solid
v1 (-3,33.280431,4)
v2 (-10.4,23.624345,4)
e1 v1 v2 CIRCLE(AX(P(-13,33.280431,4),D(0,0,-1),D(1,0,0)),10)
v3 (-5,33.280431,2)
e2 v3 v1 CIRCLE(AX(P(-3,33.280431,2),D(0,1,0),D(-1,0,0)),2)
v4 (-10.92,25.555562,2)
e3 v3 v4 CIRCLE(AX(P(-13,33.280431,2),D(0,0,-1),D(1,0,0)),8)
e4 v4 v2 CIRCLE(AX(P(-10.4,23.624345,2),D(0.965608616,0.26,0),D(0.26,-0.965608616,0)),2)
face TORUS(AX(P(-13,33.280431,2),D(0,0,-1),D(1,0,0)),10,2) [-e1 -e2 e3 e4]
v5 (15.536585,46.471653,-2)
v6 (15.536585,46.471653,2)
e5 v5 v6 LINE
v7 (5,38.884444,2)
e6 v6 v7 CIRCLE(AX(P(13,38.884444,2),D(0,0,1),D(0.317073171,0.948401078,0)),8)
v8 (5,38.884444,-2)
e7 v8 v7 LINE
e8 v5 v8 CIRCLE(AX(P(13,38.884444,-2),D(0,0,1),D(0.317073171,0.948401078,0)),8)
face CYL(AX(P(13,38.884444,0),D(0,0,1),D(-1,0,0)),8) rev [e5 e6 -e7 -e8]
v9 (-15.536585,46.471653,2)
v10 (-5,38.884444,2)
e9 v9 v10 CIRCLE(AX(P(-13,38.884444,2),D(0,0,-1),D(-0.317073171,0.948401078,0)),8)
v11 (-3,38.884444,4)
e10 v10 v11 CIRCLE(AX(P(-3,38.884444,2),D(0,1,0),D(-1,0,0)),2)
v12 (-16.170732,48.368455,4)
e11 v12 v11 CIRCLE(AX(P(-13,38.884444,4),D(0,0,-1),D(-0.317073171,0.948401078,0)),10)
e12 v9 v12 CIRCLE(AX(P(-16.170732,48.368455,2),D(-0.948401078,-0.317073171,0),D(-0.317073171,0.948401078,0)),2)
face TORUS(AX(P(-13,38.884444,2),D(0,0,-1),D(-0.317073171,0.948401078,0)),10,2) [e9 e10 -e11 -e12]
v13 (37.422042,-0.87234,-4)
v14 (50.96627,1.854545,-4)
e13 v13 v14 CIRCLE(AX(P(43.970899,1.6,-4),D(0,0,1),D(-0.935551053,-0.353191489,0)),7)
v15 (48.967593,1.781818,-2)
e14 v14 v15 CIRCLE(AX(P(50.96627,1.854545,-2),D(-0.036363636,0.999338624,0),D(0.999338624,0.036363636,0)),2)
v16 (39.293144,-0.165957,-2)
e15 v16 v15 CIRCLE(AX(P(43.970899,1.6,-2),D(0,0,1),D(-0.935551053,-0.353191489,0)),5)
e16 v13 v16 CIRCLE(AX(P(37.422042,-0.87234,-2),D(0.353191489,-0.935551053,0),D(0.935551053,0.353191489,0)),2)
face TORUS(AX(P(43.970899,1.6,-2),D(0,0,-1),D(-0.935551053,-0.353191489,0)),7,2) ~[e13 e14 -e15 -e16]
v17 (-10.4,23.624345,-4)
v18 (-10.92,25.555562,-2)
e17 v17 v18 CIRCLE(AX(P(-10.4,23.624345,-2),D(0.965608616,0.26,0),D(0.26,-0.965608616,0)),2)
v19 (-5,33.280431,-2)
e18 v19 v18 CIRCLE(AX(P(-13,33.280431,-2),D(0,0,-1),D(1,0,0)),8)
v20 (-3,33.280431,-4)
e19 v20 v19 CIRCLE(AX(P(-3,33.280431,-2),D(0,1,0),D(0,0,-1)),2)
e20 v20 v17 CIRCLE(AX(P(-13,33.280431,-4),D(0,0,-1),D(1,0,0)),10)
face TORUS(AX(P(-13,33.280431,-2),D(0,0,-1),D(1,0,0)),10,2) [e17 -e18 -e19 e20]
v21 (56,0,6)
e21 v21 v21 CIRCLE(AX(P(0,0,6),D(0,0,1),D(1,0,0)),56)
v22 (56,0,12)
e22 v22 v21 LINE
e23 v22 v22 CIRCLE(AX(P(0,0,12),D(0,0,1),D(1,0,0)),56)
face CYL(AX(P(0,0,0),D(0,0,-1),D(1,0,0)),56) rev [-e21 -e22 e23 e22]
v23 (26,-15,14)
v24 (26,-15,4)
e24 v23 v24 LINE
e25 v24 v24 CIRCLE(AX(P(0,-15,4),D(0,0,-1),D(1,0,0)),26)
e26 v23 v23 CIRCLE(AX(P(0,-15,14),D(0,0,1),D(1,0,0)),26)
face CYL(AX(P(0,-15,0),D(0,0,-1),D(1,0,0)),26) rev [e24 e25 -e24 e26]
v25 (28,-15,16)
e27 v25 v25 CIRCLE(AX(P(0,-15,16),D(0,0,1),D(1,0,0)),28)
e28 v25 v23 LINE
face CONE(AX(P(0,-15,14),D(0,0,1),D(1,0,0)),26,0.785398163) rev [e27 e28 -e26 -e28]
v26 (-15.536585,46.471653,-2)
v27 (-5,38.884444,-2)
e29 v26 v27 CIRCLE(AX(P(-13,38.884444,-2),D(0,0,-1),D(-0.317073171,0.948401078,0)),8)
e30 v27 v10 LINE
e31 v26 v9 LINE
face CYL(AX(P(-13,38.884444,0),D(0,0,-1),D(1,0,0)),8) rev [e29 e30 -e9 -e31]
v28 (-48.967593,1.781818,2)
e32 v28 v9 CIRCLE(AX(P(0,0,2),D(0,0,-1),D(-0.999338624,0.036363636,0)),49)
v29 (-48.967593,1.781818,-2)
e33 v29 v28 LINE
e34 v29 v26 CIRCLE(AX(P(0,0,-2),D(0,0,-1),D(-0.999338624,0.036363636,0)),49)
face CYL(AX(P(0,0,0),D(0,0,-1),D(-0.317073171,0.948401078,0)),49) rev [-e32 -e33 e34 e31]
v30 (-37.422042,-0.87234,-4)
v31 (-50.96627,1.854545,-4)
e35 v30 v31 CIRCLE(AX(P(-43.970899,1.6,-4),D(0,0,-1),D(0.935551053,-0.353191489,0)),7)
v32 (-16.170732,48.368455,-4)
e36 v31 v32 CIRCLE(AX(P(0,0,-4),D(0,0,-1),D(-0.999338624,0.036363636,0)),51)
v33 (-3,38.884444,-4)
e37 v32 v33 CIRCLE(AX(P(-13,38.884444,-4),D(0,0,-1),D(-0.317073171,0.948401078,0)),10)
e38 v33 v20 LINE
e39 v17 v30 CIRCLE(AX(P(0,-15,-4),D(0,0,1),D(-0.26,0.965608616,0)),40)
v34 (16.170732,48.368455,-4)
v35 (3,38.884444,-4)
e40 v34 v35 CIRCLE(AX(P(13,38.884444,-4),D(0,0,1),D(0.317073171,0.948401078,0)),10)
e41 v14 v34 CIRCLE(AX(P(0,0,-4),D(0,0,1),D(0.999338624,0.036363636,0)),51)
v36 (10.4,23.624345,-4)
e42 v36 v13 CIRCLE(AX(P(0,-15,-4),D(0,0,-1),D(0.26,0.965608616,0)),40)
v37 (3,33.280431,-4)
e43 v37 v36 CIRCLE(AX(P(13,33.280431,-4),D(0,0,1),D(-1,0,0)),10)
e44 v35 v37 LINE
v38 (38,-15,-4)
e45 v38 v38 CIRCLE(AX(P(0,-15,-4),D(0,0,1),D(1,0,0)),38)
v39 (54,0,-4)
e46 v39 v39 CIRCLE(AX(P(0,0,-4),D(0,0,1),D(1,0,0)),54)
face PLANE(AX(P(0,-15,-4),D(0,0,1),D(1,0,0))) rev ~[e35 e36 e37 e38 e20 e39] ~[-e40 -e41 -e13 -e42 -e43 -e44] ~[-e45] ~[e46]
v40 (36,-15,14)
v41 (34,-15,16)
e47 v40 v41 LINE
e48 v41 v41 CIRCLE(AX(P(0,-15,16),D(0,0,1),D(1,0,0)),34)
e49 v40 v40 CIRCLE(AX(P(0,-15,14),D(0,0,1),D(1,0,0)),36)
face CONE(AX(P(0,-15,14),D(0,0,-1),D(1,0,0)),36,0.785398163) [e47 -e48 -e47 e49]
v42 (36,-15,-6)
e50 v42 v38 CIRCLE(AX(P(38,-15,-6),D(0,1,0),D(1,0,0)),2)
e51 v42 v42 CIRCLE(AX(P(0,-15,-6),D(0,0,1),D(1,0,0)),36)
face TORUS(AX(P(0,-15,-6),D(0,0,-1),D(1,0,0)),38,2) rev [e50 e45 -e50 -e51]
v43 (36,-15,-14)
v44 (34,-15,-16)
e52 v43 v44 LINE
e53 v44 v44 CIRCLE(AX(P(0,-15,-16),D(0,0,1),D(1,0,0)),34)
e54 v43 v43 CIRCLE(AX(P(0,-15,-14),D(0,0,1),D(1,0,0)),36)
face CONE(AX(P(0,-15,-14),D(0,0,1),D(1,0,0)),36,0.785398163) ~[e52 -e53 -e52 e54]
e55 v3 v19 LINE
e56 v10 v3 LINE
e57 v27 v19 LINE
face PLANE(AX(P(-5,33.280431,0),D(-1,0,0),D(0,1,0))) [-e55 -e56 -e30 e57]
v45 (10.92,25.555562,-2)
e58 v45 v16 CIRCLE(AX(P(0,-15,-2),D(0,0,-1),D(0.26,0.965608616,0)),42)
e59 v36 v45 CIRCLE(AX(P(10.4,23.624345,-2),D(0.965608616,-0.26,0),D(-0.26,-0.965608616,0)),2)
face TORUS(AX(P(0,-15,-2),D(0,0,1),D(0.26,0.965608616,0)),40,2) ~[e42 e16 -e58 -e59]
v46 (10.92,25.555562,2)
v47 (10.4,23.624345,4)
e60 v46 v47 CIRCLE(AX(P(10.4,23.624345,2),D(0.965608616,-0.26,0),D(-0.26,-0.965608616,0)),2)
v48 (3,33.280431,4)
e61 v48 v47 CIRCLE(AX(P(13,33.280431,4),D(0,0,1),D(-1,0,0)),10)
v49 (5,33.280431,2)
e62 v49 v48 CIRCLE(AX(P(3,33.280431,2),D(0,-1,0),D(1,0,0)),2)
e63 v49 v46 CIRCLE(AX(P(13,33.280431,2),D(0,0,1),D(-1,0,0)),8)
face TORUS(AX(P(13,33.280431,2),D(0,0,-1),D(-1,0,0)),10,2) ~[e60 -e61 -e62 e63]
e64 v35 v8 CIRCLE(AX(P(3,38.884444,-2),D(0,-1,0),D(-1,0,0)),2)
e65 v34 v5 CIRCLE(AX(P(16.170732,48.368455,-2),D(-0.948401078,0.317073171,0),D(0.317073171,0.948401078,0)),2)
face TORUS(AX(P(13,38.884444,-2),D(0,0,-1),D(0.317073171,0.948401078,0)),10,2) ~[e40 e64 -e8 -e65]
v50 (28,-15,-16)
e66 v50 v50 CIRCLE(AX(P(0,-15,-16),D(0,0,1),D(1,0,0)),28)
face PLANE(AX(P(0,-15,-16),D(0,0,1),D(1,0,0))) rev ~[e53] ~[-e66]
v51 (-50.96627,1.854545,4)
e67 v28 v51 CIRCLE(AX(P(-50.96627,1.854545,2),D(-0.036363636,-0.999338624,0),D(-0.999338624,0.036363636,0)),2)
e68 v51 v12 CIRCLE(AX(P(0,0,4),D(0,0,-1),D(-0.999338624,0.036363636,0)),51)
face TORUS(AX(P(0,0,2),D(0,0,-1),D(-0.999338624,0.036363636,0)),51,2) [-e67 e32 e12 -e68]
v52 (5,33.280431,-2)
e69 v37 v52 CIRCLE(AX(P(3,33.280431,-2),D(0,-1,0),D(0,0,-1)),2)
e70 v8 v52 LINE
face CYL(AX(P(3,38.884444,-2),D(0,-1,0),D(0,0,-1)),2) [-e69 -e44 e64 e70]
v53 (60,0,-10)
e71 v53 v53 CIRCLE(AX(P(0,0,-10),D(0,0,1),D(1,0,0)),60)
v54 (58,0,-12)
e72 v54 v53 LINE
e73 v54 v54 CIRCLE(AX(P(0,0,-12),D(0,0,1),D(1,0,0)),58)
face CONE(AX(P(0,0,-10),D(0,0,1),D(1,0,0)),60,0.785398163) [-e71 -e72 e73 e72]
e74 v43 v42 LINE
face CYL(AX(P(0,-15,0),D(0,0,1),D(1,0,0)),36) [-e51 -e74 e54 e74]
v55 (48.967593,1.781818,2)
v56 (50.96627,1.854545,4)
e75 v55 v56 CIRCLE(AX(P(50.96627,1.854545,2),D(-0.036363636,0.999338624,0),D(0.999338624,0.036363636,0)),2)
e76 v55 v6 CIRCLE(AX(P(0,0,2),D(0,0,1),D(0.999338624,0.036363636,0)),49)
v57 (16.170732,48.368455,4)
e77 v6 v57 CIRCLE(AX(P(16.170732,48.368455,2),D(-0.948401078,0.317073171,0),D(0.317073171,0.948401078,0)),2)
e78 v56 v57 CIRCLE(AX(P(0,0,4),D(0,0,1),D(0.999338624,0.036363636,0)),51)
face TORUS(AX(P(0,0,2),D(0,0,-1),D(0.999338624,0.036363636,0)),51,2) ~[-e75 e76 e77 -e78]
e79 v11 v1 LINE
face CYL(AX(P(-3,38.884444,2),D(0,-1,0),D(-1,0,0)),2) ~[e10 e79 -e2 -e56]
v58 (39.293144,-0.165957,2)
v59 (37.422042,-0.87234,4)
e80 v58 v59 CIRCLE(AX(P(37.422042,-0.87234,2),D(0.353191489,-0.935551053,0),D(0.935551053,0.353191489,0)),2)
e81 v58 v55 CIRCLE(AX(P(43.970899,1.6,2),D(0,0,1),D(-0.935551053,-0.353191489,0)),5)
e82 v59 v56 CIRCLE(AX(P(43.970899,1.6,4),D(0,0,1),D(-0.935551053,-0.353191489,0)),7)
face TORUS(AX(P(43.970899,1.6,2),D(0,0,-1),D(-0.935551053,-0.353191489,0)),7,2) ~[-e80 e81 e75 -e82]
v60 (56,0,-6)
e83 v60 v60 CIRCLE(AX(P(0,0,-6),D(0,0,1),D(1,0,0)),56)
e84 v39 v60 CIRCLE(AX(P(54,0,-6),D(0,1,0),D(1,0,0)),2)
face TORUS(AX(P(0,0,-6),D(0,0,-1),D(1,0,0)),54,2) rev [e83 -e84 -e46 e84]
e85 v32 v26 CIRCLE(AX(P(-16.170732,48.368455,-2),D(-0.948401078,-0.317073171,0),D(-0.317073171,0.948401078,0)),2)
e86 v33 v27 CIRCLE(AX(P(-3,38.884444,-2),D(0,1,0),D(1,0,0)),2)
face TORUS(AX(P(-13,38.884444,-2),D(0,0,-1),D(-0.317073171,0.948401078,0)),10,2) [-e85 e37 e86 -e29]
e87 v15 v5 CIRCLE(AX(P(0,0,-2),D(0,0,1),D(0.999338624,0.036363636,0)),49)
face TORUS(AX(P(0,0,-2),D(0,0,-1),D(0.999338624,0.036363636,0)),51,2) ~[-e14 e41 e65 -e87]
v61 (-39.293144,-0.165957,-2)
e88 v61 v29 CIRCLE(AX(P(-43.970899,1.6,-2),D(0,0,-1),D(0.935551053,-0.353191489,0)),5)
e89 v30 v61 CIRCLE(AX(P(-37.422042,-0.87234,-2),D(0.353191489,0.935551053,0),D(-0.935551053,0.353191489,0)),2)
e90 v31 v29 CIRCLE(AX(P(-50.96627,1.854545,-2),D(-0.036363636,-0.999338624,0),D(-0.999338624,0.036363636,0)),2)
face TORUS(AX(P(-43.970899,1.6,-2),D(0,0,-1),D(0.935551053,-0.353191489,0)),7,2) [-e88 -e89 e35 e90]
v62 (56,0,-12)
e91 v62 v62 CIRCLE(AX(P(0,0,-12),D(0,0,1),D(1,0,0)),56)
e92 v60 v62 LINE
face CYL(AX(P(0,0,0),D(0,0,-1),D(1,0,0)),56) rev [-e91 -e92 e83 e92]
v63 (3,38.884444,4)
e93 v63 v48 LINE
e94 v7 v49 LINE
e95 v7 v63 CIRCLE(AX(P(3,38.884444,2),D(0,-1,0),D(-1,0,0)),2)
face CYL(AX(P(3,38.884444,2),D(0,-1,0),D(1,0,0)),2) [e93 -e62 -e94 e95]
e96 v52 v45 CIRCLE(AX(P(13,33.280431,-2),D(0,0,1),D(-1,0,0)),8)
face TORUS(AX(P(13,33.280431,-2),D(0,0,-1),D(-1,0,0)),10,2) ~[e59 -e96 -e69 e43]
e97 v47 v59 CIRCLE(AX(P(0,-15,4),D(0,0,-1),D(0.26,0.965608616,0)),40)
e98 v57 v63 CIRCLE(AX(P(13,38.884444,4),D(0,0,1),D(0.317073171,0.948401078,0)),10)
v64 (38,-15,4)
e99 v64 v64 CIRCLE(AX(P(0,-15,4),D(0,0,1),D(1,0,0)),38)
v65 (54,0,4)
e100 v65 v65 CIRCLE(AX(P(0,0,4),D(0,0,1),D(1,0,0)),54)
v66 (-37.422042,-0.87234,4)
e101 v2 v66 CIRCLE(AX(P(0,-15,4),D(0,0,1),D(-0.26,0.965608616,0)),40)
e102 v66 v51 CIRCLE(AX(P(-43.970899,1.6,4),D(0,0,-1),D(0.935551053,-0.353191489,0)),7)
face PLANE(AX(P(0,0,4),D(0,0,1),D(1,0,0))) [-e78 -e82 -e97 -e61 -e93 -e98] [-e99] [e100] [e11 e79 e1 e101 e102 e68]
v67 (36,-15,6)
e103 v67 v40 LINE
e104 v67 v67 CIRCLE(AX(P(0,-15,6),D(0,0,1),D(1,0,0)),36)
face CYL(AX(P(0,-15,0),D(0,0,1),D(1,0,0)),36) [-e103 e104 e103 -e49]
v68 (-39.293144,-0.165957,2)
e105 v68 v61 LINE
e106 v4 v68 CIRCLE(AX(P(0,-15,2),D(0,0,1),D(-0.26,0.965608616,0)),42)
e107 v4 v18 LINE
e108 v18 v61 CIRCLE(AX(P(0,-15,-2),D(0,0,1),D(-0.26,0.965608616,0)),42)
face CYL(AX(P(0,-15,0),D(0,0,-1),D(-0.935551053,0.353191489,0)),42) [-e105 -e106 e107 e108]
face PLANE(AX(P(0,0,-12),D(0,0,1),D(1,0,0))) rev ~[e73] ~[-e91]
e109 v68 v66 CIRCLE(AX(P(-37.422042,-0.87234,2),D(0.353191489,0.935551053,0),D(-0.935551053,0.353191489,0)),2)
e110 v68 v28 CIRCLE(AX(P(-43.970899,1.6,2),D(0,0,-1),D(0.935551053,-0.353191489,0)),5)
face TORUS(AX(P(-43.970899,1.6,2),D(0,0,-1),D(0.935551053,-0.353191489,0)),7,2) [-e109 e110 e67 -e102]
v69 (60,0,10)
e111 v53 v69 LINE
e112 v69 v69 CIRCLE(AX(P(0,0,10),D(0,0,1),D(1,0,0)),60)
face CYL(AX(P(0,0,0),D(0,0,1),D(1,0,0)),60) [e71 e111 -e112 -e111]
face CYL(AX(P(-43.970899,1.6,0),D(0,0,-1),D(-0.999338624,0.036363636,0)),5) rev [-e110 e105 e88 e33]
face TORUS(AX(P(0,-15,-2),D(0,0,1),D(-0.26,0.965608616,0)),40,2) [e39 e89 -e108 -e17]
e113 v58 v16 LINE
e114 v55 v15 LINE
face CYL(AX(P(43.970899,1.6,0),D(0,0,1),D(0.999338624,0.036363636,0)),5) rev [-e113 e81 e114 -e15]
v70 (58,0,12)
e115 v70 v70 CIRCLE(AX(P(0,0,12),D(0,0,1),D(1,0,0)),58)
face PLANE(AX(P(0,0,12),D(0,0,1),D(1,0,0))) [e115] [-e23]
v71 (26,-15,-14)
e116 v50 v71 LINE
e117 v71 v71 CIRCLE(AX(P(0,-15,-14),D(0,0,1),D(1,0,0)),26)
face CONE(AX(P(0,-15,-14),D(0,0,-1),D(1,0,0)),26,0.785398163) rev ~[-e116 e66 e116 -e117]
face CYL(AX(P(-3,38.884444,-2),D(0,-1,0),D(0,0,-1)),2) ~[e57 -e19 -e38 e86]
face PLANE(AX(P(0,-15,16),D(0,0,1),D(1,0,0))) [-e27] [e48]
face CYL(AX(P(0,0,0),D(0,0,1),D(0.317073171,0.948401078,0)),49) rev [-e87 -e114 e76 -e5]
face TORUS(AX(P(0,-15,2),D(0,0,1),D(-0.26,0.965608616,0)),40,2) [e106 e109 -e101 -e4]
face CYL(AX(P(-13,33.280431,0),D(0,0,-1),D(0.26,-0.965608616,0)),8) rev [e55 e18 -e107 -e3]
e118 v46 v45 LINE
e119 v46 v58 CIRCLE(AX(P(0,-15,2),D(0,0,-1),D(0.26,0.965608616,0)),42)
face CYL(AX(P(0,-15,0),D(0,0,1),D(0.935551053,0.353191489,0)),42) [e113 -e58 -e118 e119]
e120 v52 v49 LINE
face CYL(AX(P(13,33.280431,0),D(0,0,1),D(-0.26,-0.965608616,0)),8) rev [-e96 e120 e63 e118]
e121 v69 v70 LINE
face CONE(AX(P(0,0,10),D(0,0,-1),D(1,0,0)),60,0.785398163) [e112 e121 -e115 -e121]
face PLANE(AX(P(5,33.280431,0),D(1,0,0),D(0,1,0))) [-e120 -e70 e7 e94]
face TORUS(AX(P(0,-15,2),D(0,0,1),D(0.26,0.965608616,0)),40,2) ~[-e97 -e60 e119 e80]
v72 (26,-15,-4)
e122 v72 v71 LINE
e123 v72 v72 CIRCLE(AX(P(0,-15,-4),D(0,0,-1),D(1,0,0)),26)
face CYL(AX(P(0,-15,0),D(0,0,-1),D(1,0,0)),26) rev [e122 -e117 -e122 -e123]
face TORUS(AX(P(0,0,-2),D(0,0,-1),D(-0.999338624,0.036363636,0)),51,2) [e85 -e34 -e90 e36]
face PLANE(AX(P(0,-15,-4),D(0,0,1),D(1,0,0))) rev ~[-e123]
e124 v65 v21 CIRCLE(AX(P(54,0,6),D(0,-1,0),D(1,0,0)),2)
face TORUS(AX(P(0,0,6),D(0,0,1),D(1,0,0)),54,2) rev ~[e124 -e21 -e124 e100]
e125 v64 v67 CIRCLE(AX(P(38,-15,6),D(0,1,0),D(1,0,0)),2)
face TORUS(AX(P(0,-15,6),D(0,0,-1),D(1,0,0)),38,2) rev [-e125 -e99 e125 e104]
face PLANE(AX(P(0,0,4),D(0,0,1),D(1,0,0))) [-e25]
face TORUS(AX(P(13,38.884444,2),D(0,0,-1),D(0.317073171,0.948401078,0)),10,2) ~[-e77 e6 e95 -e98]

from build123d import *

# Parameters (mm, degrees)
DISC_RING_PROFILES_SKETCH_R   = 56
DISC_RING_PROFILES_SKETCH_R_2 = 36
DISC_RING_PROFILES_SKETCH_R_3 = 26
BASE_WEB_8MM_DEPTH            = 4
SKETCH3_3_R                   = 60
SKETCH3_3_R_2                 = 56
HUB_RING_24MM_DEPTH           = 12
SKETCH3_4_R                   = 36
SKETCH3_4_R_2                 = 26
OUTER_RIM_32MM_DEPTH          = 16
WEB_CUTOUTS_DEPTH             = 17
WEB_EDGE_FILLET_R2_R          = 2
RING_EDGE_CHAMFERS_2X45_SIZE  = 2


with BuildPart() as part:
    # Disc Ring Profiles Sketch → Base Web 8mm (new, symmetric)
    # profile 1 of 3: a face of its own
    with BuildSketch(Plane.XY):
        Circle(DISC_RING_PROFILES_SKETCH_R)
        with Locations((0, -15)):
            Circle(DISC_RING_PROFILES_SKETCH_R_2, mode=Mode.SUBTRACT)
    # profile 2 of 3: a face of its own
    with BuildSketch(Plane.XY):
        with Locations((0, -15)):
            Circle(DISC_RING_PROFILES_SKETCH_R_2)
        with Locations((0, -15)):
            Circle(DISC_RING_PROFILES_SKETCH_R_3, mode=Mode.SUBTRACT)
    # profile 3 of 3: a face of its own
    with BuildSketch(Plane.XY):
        with Locations((0, -15)):
            Circle(DISC_RING_PROFILES_SKETCH_R_3)
    extrude(amount=BASE_WEB_8MM_DEPTH, both=True)

    # Sketch3_3 → Hub Ring 24mm (add, symmetric)
    with BuildSketch(Plane.XY):
        Circle(SKETCH3_3_R)
        Circle(SKETCH3_3_R_2, mode=Mode.SUBTRACT)
    extrude(amount=HUB_RING_24MM_DEPTH, both=True)

    # Sketch3_4 → Outer Rim 32mm (add, symmetric)
    with BuildSketch(Plane.XY):
        with Locations((0, -15)):
            Circle(SKETCH3_4_R)
        with Locations((0, -15)):
            Circle(SKETCH3_4_R_2, mode=Mode.SUBTRACT)
    extrude(amount=OUTER_RIM_32MM_DEPTH, both=True)

    # Web Cutouts Sketch → Web Cutouts (cut, symmetric)
    with BuildSketch(Plane.XY):
        with BuildLine():
            Line((-5, 33.280430818), (-5, 38.88444419))
            ThreePointArc((-5, 38.88444419), (-8.325210322, 45.37646556), (-15.536585366, 46.471652813))
            ThreePointArc((-15.536585366, 46.471652813), (-39.236367993, 29.351446757), (-48.967592589, 1.781818182))
            ThreePointArc((-48.967592589, 1.781818182), (-44.957757013, -3.301643825), (-39.293144205, -0.165957447))
            ThreePointArc((-39.293144205, -0.165957447), (-28.208847937, 16.11689088), (-10.92, 25.555561887))
            ThreePointArc((-10.92, 25.555561887), (-6.650196853, 28.414220794), (-5, 33.280430818))
        make_face()
        with BuildLine():
            ThreePointArc((15.536585366, 46.471652813), (39.236367993, 29.351446757), (48.967592589, 1.781818182))
            ThreePointArc((48.967592589, 1.781818182), (44.957757013, -3.301643825), (39.293144205, -0.165957447))
            ThreePointArc((39.293144205, -0.165957447), (28.208847937, 16.11689088), (10.92, 25.555561887))
            ThreePointArc((10.92, 25.555561887), (6.650196853, 28.414220794), (5, 33.280430818))
            Line((5, 33.280430818), (5, 38.88444419))
            ThreePointArc((5, 38.88444419), (8.325210322, 45.37646556), (15.536585366, 46.471652813))
        make_face()
    extrude(amount=WEB_CUTOUTS_DEPTH, both=True, mode=Mode.SUBTRACT)

    # Web Edge Fillet R2
    web_edge_fillet_r2_edges = [part.edges().sort_by_distance(p)[0] for p in [
        (-36, -15, -4),
        (-36, -15, 4),
        (-56, 0, -4),
        (8.325210322, 45.37646556, -4),
        (5, 36.082437504, -4),
        (6.650196853, 28.414220794, -4),
        (28.208847937, 16.11689088, -4),
        (44.957757013, -3.301643825, -4),
        (39.236367993, 29.351446757, -4),
        (-8.325210322, 45.37646556, -4),
        (-39.236367993, 29.351446757, -4),
        (-44.957757013, -3.301643825, -4),
        (-28.208847937, 16.11689088, -4),
        (-6.650196853, 28.414220794, -4),
        (-5, 36.082437504, -4),
        (-5, 36.082437504, 4),
        (-6.650196853, 28.414220794, 4),
        (-28.208847937, 16.11689088, 4),
        (-44.957757013, -3.301643825, 4),
        (-39.236367993, 29.351446757, 4),
        (-8.325210322, 45.37646556, 4),
        (39.236367993, 29.351446757, 4),
        (44.957757013, -3.301643825, 4),
        (28.208847937, 16.11689088, 4),
        (6.650196853, 28.414220794, 4),
        (5, 36.082437504, 4),
        (8.325210322, 45.37646556, 4),
        (-56, 0, 4),
    ]]
    fillet(web_edge_fillet_r2_edges, radius=WEB_EDGE_FILLET_R2_R)

    # Ring Edge Chamfers 2x45
    ring_edge_chamfers_2x45_edges = [part.edges().sort_by_distance(p)[0] for p in [
        (-36, -15, -16),
        (-26, -15, 16),
        (-36, -15, 16),
        (-26, -15, -16),
        (-60, 0, -12),
        (-60, 0, 12),
    ]]
    chamfer(ring_edge_chamfers_2x45_edges, length=RING_EDGE_CHAMFERS_2X45_SIZE)


solid = part.part
